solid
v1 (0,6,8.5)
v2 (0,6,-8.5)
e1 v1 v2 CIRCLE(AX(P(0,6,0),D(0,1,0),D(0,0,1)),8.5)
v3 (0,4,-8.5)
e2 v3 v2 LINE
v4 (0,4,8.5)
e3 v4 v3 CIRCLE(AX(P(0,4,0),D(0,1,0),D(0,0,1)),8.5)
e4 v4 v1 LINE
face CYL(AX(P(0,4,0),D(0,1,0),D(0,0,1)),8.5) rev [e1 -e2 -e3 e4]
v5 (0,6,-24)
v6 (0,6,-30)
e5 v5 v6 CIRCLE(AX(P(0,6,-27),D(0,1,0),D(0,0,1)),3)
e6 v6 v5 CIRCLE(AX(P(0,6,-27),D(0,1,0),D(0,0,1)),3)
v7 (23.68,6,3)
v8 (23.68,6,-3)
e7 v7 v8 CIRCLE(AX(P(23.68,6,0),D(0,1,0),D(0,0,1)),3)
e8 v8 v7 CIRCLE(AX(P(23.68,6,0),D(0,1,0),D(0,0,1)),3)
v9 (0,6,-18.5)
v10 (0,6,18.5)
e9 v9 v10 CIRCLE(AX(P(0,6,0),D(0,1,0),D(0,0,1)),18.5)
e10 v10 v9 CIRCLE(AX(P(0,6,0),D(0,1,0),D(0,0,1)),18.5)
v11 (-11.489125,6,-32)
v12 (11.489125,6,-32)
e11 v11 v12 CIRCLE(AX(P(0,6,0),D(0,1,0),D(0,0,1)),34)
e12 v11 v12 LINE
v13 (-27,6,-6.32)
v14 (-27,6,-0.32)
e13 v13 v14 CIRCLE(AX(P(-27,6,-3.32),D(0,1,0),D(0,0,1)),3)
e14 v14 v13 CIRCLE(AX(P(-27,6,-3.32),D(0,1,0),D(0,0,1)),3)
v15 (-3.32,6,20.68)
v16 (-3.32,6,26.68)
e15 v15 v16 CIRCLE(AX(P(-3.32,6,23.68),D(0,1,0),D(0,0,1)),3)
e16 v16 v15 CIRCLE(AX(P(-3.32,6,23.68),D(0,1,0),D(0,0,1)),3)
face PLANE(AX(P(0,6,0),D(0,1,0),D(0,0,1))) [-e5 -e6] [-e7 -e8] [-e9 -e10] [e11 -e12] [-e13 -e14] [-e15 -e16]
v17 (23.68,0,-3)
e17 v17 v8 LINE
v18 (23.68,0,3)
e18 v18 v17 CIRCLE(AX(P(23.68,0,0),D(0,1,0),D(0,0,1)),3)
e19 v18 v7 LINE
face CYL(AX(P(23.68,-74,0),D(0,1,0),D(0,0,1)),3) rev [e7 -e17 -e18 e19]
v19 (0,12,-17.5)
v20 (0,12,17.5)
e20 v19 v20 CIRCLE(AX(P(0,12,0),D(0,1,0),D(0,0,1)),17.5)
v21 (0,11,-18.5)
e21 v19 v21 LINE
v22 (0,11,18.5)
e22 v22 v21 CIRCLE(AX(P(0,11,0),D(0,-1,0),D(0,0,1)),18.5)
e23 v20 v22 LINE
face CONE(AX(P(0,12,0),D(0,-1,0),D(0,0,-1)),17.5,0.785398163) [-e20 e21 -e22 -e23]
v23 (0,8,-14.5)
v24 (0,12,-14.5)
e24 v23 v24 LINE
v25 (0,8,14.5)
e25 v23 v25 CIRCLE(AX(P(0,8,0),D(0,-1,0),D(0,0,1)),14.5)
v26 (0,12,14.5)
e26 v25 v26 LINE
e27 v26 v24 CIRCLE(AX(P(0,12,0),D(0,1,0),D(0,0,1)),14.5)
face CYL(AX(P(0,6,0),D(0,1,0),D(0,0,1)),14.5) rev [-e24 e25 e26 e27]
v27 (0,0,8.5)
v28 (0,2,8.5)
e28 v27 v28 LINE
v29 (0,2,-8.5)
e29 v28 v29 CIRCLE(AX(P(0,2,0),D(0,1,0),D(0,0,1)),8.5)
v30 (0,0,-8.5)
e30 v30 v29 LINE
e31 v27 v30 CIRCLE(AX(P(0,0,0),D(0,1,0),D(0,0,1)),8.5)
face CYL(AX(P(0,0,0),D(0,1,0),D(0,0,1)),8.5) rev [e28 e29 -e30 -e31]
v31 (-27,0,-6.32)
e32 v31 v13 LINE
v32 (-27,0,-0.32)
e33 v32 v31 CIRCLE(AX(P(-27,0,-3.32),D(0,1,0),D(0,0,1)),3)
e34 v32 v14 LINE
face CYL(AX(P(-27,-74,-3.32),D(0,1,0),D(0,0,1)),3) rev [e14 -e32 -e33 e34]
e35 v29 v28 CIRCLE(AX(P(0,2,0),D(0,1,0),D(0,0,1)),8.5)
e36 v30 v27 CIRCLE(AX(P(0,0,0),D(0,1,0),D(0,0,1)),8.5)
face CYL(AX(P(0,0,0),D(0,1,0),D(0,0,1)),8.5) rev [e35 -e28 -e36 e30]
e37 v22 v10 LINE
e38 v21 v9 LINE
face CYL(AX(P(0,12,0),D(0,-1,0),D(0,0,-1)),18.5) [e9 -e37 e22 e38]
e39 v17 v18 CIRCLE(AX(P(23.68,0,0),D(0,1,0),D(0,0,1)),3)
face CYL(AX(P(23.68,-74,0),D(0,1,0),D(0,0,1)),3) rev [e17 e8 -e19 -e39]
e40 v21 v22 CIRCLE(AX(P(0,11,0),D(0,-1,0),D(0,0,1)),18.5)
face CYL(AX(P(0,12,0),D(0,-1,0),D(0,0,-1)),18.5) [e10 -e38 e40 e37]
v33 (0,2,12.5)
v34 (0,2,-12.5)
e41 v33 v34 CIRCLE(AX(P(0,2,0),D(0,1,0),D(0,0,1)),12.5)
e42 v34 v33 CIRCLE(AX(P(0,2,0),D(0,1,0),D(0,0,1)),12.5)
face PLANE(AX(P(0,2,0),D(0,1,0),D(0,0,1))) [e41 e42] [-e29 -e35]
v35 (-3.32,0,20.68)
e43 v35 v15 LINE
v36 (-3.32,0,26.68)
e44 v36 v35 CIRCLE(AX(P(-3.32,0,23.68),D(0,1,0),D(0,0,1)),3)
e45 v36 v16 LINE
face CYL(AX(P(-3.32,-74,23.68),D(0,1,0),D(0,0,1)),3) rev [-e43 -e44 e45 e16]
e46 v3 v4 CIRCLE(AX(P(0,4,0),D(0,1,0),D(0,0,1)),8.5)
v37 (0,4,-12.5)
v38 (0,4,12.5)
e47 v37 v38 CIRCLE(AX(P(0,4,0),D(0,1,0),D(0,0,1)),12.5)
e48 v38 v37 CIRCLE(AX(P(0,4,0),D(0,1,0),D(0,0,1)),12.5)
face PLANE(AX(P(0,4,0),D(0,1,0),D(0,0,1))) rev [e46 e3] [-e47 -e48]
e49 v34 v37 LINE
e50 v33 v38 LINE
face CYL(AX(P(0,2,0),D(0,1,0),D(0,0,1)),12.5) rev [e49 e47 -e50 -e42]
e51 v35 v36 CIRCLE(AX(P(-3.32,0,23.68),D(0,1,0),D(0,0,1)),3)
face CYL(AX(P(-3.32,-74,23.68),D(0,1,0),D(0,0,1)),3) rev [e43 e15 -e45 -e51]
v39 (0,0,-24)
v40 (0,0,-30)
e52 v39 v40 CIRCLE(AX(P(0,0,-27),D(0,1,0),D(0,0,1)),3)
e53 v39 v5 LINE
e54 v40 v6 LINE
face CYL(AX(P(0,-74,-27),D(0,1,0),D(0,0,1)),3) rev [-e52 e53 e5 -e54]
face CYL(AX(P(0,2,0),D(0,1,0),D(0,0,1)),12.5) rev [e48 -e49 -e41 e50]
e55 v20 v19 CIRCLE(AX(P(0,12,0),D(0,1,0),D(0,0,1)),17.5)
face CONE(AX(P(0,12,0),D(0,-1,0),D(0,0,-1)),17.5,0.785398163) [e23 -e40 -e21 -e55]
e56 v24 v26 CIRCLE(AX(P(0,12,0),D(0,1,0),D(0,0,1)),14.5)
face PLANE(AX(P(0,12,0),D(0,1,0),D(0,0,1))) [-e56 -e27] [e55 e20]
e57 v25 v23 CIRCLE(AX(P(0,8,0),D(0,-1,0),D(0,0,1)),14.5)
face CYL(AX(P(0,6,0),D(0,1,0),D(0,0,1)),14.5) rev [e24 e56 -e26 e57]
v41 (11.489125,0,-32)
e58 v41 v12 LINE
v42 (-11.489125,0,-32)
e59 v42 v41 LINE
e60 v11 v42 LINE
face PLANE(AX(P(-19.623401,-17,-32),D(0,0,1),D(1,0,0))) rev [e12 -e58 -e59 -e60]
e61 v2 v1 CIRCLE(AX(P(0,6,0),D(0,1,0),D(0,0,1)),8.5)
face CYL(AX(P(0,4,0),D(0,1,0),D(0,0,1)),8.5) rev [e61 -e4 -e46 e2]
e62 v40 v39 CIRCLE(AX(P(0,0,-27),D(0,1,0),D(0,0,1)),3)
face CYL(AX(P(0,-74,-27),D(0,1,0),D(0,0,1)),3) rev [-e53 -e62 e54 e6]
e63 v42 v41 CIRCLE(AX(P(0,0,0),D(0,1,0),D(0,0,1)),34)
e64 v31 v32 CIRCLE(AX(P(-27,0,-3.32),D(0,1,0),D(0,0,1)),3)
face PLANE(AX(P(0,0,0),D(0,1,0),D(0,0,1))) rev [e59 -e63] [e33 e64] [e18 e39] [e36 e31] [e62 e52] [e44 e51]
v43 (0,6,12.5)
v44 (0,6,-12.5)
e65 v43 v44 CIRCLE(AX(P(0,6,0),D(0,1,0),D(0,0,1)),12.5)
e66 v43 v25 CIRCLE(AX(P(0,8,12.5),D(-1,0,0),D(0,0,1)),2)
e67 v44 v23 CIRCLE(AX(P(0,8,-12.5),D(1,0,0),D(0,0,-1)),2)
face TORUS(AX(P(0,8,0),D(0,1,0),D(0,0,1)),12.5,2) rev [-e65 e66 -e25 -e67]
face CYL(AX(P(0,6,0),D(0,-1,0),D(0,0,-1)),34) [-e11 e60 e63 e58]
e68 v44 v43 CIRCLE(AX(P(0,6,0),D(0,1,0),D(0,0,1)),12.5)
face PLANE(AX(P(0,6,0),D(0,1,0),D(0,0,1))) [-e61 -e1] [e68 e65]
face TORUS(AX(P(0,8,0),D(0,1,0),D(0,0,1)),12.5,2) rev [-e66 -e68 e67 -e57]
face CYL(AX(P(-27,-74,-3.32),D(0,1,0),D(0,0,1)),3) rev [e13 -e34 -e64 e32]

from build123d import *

# Parameters (mm, degrees)
SKETCH1_R           = 34
BOSS_EXTRUDE1_DEPTH = 6
SKETCH2_R           = 18.5
BOSS_EXTRUDE2_DEPTH = 6
SKETCH3_R           = 14.5
CUT_EXTRUDE1_DEPTH  = 6
SKETCH4_R           = 8.5
CUT_EXTRUDE2_DEPTH  = 2
SKETCH5_R           = 12.5
CUT_EXTRUDE3_DEPTH  = 2
SKETCH6_R           = 8.5
CUT_EXTRUDE4_DEPTH  = 2
CHAMFER1_SIZE       = 1
FILLET1_R           = 2
SKETCH7_W           = 39.246802542
SKETCH7_H           = 4
CUT_EXTRUDE5_DEPTH  = 23
SKETCH8_R           = 3
CUT_EXTRUDE6_DEPTH  = 80


with BuildPart() as part:
    # Sketch1 → Boss-Extrude1 (new body)
    with BuildSketch(Plane(origin=(0, 0, 0), x_dir=(1, 0, 0), z_dir=(0, 1, 0))):
        with Locations(Location((0, 0, 0), (0, 0, 270))):
            Circle(SKETCH1_R)
    extrude(amount=BOSS_EXTRUDE1_DEPTH)

    # Sketch2 → Boss-Extrude2 (add)
    with BuildSketch(Plane(origin=(0, 6, 0), x_dir=(1, 0, 0), z_dir=(0, 1, 0))):
        with Locations(Location((0, 0, 0), (0, 0, 270))):
            Circle(SKETCH2_R)
    extrude(amount=BOSS_EXTRUDE2_DEPTH)

    # Sketch3 → Cut-Extrude1 (cut)
    with BuildSketch(Plane(origin=(0, 12, 0), x_dir=(1, 0, 0), z_dir=(0, 1, 0))):
        with Locations(Location((0, 0, 0), (0, 0, 270))):
            Circle(SKETCH3_R)
    extrude(amount=-CUT_EXTRUDE1_DEPTH, mode=Mode.SUBTRACT)

    # Sketch4 → Cut-Extrude2 (cut)
    with BuildSketch(Plane(origin=(0, 6, 0), x_dir=(1, 0, 0), z_dir=(0, 1, 0))):
        with Locations(Location((0, 0, 0), (0, 0, 270))):
            Circle(SKETCH4_R)
    extrude(amount=-CUT_EXTRUDE2_DEPTH, mode=Mode.SUBTRACT)

    # Sketch5 → Cut-Extrude3 (cut)
    with BuildSketch(Plane(origin=(0, 4, 0), x_dir=(1, 0, 0), z_dir=(0, 1, 0))):
        with Locations(Location((0, 0, 0), (0, 0, 270))):
            Circle(SKETCH5_R)
    extrude(amount=-CUT_EXTRUDE3_DEPTH, mode=Mode.SUBTRACT)

    # Sketch6 → Cut-Extrude4 (cut)
    with BuildSketch(Plane(origin=(0, 2, 0), x_dir=(1, 0, 0), z_dir=(0, 1, 0))):
        with Locations(Location((0, 0, 0), (0, 0, 270))):
            Circle(SKETCH6_R)
    extrude(amount=-CUT_EXTRUDE4_DEPTH, mode=Mode.SUBTRACT)

    # Chamfer1
    chamfer1_edges = [part.edges().sort_by_distance(p)[0] for p in [
        (0, 12, -18.5),
    ]]
    chamfer(chamfer1_edges, length=CHAMFER1_SIZE)

    # Fillet1
    fillet1_edges = [part.edges().sort_by_distance(p)[0] for p in [
        (0, 6, -14.5),
    ]]
    fillet(fillet1_edges, radius=FILLET1_R)

    # Sketch7 → Cut-Extrude5 (cut)
    with BuildSketch(Plane(origin=(0, 6, 0), x_dir=(1, 0, 0), z_dir=(0, 1, 0))):
        with Locations((0, 34)):
            Rectangle(SKETCH7_W, SKETCH7_H)
    extrude(amount=-CUT_EXTRUDE5_DEPTH, mode=Mode.SUBTRACT)

    # Sketch8 → Cut-Extrude6 (cut)
    with BuildSketch(Plane(origin=(0, 6, 0), x_dir=(1, 0, 0), z_dir=(0, 1, 0))):
        with Locations(Location((0, 27, 0), (0, 0, 270))):
            Circle(SKETCH8_R)
        with Locations(Location((23.68, 0, 0), (0, 0, 270))):
            Circle(SKETCH8_R)
        with Locations(Location((-3.32, -23.68, 0), (0, 0, 270))):
            Circle(SKETCH8_R)
        with Locations(Location((-27, 3.32, 0), (0, 0, 270))):
            Circle(SKETCH8_R)
    extrude(amount=-CUT_EXTRUDE6_DEPTH, mode=Mode.SUBTRACT)


solid = part.part
